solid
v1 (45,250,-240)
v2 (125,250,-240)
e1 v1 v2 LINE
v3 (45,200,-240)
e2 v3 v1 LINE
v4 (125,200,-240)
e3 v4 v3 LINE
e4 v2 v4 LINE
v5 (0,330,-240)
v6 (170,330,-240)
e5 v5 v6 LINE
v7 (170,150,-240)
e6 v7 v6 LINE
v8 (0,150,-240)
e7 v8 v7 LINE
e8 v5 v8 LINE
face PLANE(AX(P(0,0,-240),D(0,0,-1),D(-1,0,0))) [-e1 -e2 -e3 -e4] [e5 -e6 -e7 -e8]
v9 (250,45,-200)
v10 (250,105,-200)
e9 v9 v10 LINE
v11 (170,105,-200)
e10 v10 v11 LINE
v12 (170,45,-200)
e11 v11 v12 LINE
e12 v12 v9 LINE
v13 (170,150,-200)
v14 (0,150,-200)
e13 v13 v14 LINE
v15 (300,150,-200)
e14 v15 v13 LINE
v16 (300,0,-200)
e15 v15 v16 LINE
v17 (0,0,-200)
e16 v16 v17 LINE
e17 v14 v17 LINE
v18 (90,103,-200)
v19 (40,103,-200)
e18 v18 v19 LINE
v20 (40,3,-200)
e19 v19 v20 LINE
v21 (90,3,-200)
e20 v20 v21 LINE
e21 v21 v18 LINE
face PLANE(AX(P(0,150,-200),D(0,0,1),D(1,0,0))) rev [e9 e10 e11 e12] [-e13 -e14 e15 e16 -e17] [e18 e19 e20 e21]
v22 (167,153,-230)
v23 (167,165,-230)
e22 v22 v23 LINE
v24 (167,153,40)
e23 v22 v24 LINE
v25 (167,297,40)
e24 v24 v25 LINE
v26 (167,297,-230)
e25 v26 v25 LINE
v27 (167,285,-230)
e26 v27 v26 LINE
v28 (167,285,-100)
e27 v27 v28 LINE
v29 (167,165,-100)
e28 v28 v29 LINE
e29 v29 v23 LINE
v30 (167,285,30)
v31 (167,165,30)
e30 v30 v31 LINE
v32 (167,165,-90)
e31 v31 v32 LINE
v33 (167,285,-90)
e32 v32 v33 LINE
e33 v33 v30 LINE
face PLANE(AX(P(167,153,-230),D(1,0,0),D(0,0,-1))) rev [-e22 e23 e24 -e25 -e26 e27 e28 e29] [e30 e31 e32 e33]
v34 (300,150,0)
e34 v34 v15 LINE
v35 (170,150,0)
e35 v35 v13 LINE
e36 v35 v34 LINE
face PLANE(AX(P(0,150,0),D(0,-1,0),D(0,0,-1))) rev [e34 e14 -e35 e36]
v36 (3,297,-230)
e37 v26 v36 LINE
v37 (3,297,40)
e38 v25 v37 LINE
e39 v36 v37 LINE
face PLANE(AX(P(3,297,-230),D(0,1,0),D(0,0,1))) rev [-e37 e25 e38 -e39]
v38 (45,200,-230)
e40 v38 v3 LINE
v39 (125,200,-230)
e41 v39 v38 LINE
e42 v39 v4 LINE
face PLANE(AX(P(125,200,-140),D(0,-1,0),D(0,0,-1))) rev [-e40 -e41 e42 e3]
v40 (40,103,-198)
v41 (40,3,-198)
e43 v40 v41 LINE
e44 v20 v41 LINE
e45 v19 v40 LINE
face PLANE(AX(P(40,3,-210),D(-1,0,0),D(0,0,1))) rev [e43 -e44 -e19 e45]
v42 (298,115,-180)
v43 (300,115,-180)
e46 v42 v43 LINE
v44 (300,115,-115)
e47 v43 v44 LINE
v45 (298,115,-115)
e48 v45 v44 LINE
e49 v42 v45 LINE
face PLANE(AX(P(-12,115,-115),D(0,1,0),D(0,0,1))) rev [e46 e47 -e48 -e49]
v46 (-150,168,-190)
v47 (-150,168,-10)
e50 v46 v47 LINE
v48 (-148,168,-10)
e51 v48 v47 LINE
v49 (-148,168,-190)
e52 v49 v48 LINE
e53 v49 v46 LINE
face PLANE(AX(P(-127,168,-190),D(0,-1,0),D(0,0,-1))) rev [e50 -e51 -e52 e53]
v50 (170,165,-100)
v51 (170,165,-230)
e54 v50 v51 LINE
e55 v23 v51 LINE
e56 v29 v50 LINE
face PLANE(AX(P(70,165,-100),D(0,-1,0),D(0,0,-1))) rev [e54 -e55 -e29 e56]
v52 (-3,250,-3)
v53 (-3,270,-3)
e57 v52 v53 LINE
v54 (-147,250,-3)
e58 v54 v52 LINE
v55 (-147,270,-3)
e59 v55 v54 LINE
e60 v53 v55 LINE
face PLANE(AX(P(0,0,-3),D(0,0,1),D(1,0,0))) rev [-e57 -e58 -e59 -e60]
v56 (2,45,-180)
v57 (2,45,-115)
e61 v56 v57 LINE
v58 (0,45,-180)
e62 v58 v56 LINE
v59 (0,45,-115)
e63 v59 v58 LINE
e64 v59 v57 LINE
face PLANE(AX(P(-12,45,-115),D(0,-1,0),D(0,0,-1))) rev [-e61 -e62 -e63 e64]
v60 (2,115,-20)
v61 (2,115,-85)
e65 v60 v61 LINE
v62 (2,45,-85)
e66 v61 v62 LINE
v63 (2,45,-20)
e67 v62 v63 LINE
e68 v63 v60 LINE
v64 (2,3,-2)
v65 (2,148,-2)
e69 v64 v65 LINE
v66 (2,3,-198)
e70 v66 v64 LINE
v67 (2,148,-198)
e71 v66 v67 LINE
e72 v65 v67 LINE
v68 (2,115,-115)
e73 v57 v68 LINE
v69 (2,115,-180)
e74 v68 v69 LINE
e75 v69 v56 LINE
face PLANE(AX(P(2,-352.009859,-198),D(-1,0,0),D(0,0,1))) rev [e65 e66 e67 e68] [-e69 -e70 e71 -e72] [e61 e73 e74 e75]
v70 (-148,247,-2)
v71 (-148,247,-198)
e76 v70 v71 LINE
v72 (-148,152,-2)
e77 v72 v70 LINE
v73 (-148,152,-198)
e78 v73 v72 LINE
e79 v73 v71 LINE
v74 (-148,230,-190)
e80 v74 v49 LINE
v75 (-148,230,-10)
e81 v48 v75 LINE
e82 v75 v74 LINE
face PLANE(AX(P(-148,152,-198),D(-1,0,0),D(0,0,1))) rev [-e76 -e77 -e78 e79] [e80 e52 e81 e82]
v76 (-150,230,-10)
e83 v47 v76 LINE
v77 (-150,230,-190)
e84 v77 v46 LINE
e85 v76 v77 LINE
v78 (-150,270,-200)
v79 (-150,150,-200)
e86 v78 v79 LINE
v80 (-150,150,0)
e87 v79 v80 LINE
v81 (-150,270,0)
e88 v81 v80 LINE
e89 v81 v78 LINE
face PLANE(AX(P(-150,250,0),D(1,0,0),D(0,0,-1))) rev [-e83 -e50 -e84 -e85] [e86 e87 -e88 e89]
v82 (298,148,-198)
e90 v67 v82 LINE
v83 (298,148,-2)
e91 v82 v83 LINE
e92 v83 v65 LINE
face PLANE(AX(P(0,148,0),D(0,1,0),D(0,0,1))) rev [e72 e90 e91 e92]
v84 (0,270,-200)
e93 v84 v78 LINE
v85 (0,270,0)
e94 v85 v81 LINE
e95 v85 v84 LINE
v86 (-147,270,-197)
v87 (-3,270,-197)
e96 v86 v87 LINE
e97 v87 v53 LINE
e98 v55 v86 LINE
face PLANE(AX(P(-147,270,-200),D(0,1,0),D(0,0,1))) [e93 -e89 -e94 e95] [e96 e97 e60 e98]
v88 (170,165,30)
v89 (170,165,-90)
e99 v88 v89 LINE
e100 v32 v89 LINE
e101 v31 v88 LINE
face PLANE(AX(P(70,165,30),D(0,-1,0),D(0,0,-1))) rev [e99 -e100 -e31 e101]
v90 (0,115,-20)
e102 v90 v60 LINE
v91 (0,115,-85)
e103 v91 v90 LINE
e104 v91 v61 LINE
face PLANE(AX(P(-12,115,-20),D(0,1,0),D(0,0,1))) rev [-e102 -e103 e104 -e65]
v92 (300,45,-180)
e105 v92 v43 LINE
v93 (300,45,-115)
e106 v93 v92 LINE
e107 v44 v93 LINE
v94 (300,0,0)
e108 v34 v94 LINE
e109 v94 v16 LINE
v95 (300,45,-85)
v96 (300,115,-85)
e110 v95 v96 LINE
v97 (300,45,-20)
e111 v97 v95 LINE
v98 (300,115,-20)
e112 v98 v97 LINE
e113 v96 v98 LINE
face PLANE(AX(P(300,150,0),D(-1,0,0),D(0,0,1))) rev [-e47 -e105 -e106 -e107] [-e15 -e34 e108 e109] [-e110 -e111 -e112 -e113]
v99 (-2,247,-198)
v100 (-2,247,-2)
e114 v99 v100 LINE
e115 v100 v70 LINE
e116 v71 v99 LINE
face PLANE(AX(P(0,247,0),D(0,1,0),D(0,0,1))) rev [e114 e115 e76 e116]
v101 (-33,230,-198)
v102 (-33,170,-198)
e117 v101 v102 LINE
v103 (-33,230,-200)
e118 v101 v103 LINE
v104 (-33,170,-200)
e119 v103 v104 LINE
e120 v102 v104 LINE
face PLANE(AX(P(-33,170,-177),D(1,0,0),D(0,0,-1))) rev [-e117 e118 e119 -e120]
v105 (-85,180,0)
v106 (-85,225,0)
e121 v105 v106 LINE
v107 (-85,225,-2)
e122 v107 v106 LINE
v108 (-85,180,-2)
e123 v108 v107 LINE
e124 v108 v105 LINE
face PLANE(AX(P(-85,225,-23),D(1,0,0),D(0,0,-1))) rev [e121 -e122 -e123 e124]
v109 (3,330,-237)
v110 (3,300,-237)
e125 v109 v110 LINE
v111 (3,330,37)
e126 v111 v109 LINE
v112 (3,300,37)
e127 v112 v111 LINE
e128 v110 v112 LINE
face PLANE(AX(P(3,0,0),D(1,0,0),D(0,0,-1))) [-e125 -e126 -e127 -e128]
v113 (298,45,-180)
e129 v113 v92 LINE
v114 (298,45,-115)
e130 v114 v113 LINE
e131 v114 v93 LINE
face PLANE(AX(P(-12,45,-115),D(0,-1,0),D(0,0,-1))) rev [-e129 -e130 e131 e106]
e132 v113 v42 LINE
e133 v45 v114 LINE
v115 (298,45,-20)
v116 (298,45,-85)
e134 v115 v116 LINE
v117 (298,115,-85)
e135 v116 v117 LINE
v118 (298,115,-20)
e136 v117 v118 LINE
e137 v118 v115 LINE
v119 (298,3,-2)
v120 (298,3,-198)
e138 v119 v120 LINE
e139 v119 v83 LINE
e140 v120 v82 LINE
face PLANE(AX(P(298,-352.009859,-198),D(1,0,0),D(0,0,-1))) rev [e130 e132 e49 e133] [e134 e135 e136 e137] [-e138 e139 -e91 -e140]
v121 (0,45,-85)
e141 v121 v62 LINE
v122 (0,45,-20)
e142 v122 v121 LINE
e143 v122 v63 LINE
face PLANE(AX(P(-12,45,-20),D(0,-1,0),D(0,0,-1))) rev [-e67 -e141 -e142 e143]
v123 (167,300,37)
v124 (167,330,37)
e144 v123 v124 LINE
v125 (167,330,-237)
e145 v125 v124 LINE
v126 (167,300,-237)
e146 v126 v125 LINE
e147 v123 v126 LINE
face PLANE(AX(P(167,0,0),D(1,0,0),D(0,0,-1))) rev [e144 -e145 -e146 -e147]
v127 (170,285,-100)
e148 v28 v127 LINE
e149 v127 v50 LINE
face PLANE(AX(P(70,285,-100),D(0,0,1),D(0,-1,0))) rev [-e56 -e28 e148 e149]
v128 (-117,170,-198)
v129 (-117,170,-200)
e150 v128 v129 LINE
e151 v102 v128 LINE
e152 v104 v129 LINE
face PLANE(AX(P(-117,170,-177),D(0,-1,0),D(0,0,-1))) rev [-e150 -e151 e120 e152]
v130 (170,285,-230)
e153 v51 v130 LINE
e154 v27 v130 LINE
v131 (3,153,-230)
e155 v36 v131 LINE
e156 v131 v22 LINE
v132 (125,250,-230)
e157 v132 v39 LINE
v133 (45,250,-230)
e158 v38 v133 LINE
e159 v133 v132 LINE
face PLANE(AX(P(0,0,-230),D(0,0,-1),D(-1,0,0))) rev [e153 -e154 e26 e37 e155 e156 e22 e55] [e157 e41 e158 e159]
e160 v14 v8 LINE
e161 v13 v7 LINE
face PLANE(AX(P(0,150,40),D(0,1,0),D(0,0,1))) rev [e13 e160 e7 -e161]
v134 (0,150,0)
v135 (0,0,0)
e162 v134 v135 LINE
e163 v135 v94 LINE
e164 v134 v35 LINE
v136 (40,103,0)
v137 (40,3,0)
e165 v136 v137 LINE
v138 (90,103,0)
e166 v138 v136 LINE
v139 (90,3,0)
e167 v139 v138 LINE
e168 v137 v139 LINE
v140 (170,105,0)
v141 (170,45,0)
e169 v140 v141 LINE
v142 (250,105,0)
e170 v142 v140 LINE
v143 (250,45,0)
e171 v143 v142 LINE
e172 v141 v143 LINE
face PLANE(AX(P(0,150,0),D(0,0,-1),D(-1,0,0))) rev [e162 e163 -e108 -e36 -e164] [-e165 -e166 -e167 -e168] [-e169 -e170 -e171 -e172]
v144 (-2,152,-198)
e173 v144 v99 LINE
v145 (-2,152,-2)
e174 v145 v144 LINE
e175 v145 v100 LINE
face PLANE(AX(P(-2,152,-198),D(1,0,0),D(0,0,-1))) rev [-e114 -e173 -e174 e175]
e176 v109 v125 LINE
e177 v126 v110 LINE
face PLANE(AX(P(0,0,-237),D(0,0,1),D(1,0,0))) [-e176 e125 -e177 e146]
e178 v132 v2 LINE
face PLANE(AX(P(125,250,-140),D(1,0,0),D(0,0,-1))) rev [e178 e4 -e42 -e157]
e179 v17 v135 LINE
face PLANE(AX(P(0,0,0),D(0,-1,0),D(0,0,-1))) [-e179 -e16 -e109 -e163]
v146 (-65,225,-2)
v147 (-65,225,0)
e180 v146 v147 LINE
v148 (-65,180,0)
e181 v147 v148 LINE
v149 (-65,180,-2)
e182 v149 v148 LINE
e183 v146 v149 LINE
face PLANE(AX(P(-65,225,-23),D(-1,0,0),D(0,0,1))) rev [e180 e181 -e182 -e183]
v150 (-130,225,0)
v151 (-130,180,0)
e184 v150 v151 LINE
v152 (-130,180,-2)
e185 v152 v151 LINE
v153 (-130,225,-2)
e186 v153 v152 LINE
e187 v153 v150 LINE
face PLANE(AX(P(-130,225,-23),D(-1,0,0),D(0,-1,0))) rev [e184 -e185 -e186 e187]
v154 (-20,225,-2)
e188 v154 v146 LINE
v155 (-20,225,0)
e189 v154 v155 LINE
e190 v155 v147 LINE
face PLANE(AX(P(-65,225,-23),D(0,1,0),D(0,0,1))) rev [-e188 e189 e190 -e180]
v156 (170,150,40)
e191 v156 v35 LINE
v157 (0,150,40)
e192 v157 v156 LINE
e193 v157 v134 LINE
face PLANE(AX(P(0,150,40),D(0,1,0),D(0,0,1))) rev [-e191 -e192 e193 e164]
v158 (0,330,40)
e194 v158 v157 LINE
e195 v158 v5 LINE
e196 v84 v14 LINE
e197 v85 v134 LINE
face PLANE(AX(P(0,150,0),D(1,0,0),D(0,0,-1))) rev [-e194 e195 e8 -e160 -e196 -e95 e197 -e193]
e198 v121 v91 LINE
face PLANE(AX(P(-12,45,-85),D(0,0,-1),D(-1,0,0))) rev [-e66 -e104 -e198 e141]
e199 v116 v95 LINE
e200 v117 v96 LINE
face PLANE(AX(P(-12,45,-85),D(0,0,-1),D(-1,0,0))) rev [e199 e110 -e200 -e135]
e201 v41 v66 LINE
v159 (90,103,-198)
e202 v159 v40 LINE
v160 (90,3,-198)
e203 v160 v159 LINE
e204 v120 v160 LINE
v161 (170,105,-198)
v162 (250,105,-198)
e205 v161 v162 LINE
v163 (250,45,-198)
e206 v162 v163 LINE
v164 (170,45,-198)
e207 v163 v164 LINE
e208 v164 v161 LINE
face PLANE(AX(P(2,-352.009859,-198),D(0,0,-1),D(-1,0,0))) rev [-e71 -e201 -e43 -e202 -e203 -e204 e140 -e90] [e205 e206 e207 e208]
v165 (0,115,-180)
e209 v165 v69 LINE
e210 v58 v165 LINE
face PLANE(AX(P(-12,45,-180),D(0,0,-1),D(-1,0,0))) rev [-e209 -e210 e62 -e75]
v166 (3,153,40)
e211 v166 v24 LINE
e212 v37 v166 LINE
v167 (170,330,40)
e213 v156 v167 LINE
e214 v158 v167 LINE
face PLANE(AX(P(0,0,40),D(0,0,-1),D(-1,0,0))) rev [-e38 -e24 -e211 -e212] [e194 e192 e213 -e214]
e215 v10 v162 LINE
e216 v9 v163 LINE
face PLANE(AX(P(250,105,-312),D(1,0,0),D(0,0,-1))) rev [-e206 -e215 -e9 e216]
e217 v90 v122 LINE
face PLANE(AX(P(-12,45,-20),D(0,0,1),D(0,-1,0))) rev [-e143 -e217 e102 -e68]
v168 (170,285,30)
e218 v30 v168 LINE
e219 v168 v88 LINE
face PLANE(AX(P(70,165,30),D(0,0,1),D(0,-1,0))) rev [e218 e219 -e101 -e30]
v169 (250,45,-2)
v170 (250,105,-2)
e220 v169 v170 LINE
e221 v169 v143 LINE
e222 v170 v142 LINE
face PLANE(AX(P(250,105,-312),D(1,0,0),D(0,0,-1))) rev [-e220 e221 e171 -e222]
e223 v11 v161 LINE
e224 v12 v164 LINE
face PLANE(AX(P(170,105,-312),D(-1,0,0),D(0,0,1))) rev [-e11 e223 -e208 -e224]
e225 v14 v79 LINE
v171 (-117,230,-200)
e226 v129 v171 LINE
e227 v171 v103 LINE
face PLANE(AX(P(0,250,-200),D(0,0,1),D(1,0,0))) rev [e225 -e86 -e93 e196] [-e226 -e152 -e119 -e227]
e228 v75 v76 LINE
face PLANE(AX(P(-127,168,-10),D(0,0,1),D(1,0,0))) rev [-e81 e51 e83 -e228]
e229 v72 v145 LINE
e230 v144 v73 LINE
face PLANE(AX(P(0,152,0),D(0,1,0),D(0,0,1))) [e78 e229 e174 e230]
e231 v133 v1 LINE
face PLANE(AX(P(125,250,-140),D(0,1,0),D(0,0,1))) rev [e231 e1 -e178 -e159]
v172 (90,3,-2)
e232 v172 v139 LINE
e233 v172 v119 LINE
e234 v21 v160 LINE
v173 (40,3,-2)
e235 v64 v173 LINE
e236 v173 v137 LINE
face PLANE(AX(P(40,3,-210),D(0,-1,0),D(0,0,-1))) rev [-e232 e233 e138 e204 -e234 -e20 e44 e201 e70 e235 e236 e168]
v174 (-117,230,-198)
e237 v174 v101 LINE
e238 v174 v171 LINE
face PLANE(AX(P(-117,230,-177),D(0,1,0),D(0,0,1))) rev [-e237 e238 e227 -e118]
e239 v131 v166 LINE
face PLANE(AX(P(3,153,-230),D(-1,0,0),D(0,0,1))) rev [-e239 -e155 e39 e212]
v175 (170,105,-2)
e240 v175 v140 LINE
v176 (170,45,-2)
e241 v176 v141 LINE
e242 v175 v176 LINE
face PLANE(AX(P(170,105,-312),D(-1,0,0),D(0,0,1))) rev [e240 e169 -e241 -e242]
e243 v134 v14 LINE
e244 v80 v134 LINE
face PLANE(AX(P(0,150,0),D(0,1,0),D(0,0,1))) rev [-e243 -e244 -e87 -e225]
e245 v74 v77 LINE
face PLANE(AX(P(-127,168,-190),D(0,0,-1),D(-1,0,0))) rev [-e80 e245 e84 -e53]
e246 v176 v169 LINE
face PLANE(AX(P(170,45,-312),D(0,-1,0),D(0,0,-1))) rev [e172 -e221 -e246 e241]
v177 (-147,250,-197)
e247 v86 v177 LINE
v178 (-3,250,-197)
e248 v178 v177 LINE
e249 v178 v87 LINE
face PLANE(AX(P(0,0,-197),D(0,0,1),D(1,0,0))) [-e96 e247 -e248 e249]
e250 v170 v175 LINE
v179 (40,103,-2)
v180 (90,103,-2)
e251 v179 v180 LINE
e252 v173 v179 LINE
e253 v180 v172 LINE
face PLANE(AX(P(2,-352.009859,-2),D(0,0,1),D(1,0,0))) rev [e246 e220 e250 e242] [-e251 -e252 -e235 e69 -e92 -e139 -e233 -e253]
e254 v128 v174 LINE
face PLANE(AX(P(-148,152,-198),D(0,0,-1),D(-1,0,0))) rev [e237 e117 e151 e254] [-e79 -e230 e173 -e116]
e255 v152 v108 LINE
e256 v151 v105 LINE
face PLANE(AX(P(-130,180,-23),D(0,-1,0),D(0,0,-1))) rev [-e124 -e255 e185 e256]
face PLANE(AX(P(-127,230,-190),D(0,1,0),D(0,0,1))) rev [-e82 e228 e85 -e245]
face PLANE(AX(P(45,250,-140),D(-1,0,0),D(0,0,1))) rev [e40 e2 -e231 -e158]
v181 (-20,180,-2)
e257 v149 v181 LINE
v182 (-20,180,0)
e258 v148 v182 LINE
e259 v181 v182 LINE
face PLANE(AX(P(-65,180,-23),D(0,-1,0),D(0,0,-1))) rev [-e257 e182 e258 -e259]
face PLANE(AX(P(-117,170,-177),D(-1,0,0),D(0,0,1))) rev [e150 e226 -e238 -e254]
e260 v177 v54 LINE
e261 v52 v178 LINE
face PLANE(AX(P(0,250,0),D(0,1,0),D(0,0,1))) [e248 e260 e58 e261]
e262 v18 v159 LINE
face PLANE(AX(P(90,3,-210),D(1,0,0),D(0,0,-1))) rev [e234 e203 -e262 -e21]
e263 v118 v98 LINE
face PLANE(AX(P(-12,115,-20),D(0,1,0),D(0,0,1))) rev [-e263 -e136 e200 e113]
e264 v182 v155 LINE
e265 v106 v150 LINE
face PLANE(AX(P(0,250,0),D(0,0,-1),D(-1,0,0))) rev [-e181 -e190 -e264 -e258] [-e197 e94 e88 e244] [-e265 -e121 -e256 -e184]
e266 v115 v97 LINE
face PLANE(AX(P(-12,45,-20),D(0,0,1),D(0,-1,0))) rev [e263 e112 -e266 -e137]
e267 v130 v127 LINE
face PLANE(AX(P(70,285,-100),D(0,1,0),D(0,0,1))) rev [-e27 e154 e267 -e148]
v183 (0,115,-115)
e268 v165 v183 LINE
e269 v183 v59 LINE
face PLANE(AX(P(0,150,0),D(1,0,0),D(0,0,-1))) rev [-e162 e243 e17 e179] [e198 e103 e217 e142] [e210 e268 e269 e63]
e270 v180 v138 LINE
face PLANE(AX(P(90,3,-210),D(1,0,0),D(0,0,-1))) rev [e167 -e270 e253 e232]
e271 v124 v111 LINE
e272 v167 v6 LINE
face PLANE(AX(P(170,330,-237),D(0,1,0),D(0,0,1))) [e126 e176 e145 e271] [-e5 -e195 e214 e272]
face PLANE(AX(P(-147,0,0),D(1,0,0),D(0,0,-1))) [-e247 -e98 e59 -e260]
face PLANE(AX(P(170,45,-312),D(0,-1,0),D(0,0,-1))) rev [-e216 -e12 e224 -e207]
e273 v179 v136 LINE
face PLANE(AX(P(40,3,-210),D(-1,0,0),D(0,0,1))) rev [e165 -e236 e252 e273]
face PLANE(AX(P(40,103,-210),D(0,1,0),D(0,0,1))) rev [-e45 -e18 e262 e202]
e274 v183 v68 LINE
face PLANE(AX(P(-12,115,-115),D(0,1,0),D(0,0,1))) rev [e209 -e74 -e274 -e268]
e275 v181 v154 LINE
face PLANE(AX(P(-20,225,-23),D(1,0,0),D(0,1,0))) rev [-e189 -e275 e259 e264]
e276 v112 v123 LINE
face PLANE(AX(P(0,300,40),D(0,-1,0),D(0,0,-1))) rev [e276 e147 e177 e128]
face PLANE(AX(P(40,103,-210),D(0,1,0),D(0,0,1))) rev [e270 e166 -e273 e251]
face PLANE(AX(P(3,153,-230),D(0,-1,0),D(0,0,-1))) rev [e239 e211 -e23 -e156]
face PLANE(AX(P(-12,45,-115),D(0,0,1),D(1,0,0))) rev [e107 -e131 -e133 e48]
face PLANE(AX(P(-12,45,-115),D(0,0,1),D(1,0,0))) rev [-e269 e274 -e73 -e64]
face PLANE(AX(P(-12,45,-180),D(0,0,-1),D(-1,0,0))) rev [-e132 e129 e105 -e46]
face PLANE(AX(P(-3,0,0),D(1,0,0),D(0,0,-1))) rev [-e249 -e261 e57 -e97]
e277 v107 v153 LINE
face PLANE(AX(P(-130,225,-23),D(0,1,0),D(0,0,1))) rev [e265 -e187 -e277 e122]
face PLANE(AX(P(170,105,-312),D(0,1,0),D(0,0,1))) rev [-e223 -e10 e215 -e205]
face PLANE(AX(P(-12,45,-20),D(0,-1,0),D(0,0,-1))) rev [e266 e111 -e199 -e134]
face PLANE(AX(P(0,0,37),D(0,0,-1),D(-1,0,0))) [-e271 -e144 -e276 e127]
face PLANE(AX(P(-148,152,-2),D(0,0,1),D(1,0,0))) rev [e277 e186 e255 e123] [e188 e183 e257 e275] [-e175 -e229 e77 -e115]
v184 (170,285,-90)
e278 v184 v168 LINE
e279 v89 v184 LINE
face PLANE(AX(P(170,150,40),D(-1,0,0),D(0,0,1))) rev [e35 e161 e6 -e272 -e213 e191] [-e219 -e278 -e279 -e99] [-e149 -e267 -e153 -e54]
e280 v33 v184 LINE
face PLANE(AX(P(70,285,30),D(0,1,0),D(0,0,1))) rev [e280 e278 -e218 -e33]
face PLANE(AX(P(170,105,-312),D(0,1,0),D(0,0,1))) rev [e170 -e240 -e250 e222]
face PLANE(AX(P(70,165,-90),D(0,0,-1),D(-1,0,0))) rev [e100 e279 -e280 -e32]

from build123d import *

# Parameters (mm, degrees)
GROUND_FLOOR_FOOTPRINT_SKETCH_W     = 300
GROUND_FLOOR_FOOTPRINT_SKETCH_H     = 200
GROUND_FLOOR_BLOCK_DEPTH            = 150
GROUND_FLOOR_DOOR_SKETCH_W          = 50
GROUND_FLOOR_DOOR_SKETCH_H          = 100
GROUND_FLOOR_DOOR_OPENING_DEPTH     = 210
GROUND_FLOOR_INTERIOR_POCKET_REACH  = 392.512
GROUND_FLOOR_INTERIOR_SKETCH_W      = 296
GROUND_FLOOR_INTERIOR_SKETCH_H      = 196
GROUND_FLOOR_SLAB_SKETCH_W          = 300
GROUND_FLOOR_SLAB_SKETCH_H          = 200
GROUND_FLOOR_SLAB_DEPTH             = 2
GROUND_FLOOR_WINDOW_SKETCH_W        = 80
GROUND_FLOOR_WINDOW_SKETCH_H        = 60
GROUND_FLOOR_WINDOW_DEPTH           = 312
GROUND_FLOOR_SIDE_WINDOWS_SKETCH_W  = 65
GROUND_FLOOR_SIDE_WINDOWS_SKETCH_H  = 70
GROUND_FLOOR_SIDE_WINDOWS_DEPTH     = 312
FIRST_FLOOR_FOOTPRINT_SKETCH_W      = 150
FIRST_FLOOR_FOOTPRINT_SKETCH_H      = 200
FIRST_FLOOR_BLOCK_DEPTH             = 100
FIRST_FLOOR_INTERIOR_SKETCH_W       = 146
FIRST_FLOOR_INTERIOR_SKETCH_H       = 196
FIRST_FLOOR_INTERIOR_POCKET_DEPTH   = 98
FIRST_FLOOR_SLAB_SKETCH_W           = 150
FIRST_FLOOR_SLAB_SKETCH_H           = 200
FIRST_FLOOR_SLAB_DEPTH              = 3
FIRST_FLOOR_DOOR_SKETCH_W           = 180
FIRST_FLOOR_DOOR_SKETCH_H           = 62
FIRST_FLOOR_DOOR_OPENING_DEPTH      = 23
FIRST_FLOOR_TWIN_WINDOWS_SKETCH_W   = 45
FIRST_FLOOR_TWIN_WINDOWS_SKETCH_H   = 45
FIRST_FLOOR_TWIN_WINDOWS_DEPTH      = 23
FIRST_FLOOR_WINDOW_SKETCH_W         = 84
FIRST_FLOOR_WINDOW_SKETCH_H         = 60
FIRST_FLOOR_WINDOW_DEPTH            = 23
FIRST_FLOOR_PARAPET_FRONT_SKETCH_W  = 200
FIRST_FLOOR_PARAPET_FRONT_SKETCH_H  = 20
FIRST_FLOOR_PARAPET_FRONT_DEPTH     = 3
FIRST_FLOOR_PARAPET_SIDE_1_SKETCH_W = 150
FIRST_FLOOR_PARAPET_SIDE_1_SKETCH_H = 20
FIRST_FLOOR_PARAPET_SIDE_1_DEPTH    = 3
FIRST_FLOOR_PARAPET_SIDE_2_SKETCH_W = 150
FIRST_FLOOR_PARAPET_SIDE_2_SKETCH_H = 20
FIRST_FLOOR_PARAPET_SIDE_2_DEPTH    = 3
FIRST_FLOOR_PARAPET_REAR_SKETCH_W   = 197
FIRST_FLOOR_PARAPET_REAR_SKETCH_H   = 20
FIRST_FLOOR_PARAPET_REAR_DEPTH      = 3
UPPER_FLOOR_BLOCK_DEPTH             = 40
UPPER_FLOOR_BLOCK_DEPTH_BACK        = 240
UPPER_FLOOR_PROFILE_SKETCH_W        = 170
UPPER_FLOOR_PROFILE_SKETCH_H        = 150
UPPER_FLOOR_INTERIOR_SKETCH_W       = 164
UPPER_FLOOR_INTERIOR_SKETCH_H       = 144
UPPER_FLOOR_INTERIOR_POCKET_DEPTH   = 270
UPPER_FLOOR_OPENING_1_SKETCH_W      = 120
UPPER_FLOOR_OPENING_1_SKETCH_H      = 120
UPPER_FLOOR_OPENING_1_DEPTH         = 100
UPPER_FLOOR_OPENING_2_SKETCH_W      = 130
UPPER_FLOOR_OPENING_2_SKETCH_H      = 120
UPPER_FLOOR_OPENING_2_DEPTH         = 100
UPPER_FLOOR_WINDOW_SKETCH_W         = 80
UPPER_FLOOR_WINDOW_SKETCH_H         = 50
UPPER_FLOOR_WINDOW_DEPTH            = 100
UPPER_FLOOR_PARAPET_FRONT_SKETCH_W  = 170
UPPER_FLOOR_PARAPET_FRONT_SKETCH_H  = 30
UPPER_FLOOR_PARAPET_FRONT_DEPTH     = 3
UPPER_FLOOR_PARAPET_SIDE_1_SKETCH_W = 277
UPPER_FLOOR_PARAPET_SIDE_1_SKETCH_H = 30
UPPER_FLOOR_PARAPET_SIDE_1_DEPTH    = 3
UPPER_FLOOR_PARAPET_SIDE_2_SKETCH_W = 170
UPPER_FLOOR_PARAPET_SIDE_2_SKETCH_H = 30
UPPER_FLOOR_PARAPET_SIDE_2_DEPTH    = 3
UPPER_FLOOR_PARAPET_REAR_SKETCH_W   = 274
UPPER_FLOOR_PARAPET_REAR_SKETCH_H   = 30
UPPER_FLOOR_PARAPET_REAR_DEPTH      = 3


with BuildPart() as part:
    # Ground Floor Footprint Sketch → Ground Floor Block (new body)
    with BuildSketch(Plane(origin=(0, 0, 0), x_dir=(1, 0, 0), z_dir=(0, 1, 0))):
        with Locations((150, 100)):
            Rectangle(GROUND_FLOOR_FOOTPRINT_SKETCH_W, GROUND_FLOOR_FOOTPRINT_SKETCH_H)
    extrude(amount=GROUND_FLOOR_BLOCK_DEPTH)

    # Ground Floor Door Sketch → Ground Floor Door Opening (cut)
    with BuildSketch(Plane.XY):
        with Locations((65, 53)):
            Rectangle(GROUND_FLOOR_DOOR_SKETCH_W, GROUND_FLOOR_DOOR_SKETCH_H)
    extrude(amount=-GROUND_FLOOR_DOOR_OPENING_DEPTH, mode=Mode.SUBTRACT)

    # Ground Floor Interior Pocket: up to this face of the body (flat: up to its plane)
    ground_floor_interior_pocket_end = Plane(part.part.faces().sort_by_distance((65, 3, -100))[0])
    # Ground Floor Interior Sketch → Ground Floor Interior Pocket (cut, up to the picked face)
    with BuildSketch(Plane(origin=(0, 150, 0), x_dir=(1, 0, 0), z_dir=(0, 1, 0)), mode=Mode.PRIVATE) as ground_floor_interior_pocket_sk1:
        with Locations((150, 100)):
            Rectangle(GROUND_FLOOR_INTERIOR_SKETCH_W, GROUND_FLOOR_INTERIOR_SKETCH_H)
    ground_floor_interior_pocket_tool1 = split(extrude(ground_floor_interior_pocket_sk1.sketch, amount=-GROUND_FLOOR_INTERIOR_POCKET_REACH, mode=Mode.PRIVATE), bisect_by=ground_floor_interior_pocket_end, keep=Keep.BOTH, mode=Mode.PRIVATE)
    add(ground_floor_interior_pocket_tool1.solids().sort_by(Axis((150, 150, -100), (0, -1, 0)))[0], mode=Mode.SUBTRACT)

    # Ground Floor Slab Sketch → Ground Floor Slab (add)
    with BuildSketch(Plane(origin=(0, 150, 0), x_dir=(1, 0, 0), z_dir=(0, 1, 0))):
        with Locations((150, 100)):
            Rectangle(GROUND_FLOOR_SLAB_SKETCH_W, GROUND_FLOOR_SLAB_SKETCH_H)
    extrude(amount=-GROUND_FLOOR_SLAB_DEPTH)

    # Ground Floor Window Sketch → Ground Floor Window (cut)
    with BuildSketch(Plane.XY):
        with Locations((210, 75)):
            Rectangle(GROUND_FLOOR_WINDOW_SKETCH_W, GROUND_FLOOR_WINDOW_SKETCH_H)
    extrude(amount=-GROUND_FLOOR_WINDOW_DEPTH, mode=Mode.SUBTRACT)

    # Ground Floor Side Windows Sketch → Ground Floor Side Windows (cut)
    with BuildSketch(Plane(origin=(300, 0, 0), x_dir=(0, 0, -1), z_dir=(1, 0, 0))):
        with Locations((52.5, 80)):
            Rectangle(GROUND_FLOOR_SIDE_WINDOWS_SKETCH_W, GROUND_FLOOR_SIDE_WINDOWS_SKETCH_H)
        with Locations((147.5, 80)):
            Rectangle(GROUND_FLOOR_SIDE_WINDOWS_SKETCH_W, GROUND_FLOOR_SIDE_WINDOWS_SKETCH_H)
    extrude(amount=-GROUND_FLOOR_SIDE_WINDOWS_DEPTH, mode=Mode.SUBTRACT)



with BuildPart() as body_2:
    # First Floor Footprint Sketch → First Floor Block (new body)
    with BuildSketch(Plane(origin=(0, 150, 0), x_dir=(1, 0, 0), z_dir=(0, 1, 0))):
        with Locations((-75, 100)):
            Rectangle(FIRST_FLOOR_FOOTPRINT_SKETCH_W, FIRST_FLOOR_FOOTPRINT_SKETCH_H)
    extrude(amount=FIRST_FLOOR_BLOCK_DEPTH)

    # First Floor Interior Sketch → First Floor Interior Pocket (cut)
    with BuildSketch(Plane(origin=(0, 250, 0), x_dir=(1, 0, 0), z_dir=(0, 1, 0))):
        with Locations((-75, 100)):
            Rectangle(FIRST_FLOOR_INTERIOR_SKETCH_W, FIRST_FLOOR_INTERIOR_SKETCH_H)
    extrude(amount=-FIRST_FLOOR_INTERIOR_POCKET_DEPTH, mode=Mode.SUBTRACT)

    # First Floor Slab Sketch → First Floor Slab (add)
    with BuildSketch(Plane(origin=(0, 250, 0), x_dir=(1, 0, 0), z_dir=(0, 1, 0))):
        with Locations((-75, 100)):
            Rectangle(FIRST_FLOOR_SLAB_SKETCH_W, FIRST_FLOOR_SLAB_SKETCH_H)
    extrude(amount=-FIRST_FLOOR_SLAB_DEPTH)

    # First Floor Door Sketch → First Floor Door Opening (cut)
    with BuildSketch(Plane.ZY.offset(150)):
        with Locations((-100, 199)):
            Rectangle(FIRST_FLOOR_DOOR_SKETCH_W, FIRST_FLOOR_DOOR_SKETCH_H)
    extrude(amount=-FIRST_FLOOR_DOOR_OPENING_DEPTH, mode=Mode.SUBTRACT)

    # First Floor Twin Windows Sketch → First Floor Twin Windows (cut)
    with BuildSketch(Plane.XY):
        with Locations((-107.5, 202.5)):
            Rectangle(FIRST_FLOOR_TWIN_WINDOWS_SKETCH_W, FIRST_FLOOR_TWIN_WINDOWS_SKETCH_H)
        with Locations((-42.5, 202.5)):
            Rectangle(FIRST_FLOOR_TWIN_WINDOWS_SKETCH_W, FIRST_FLOOR_TWIN_WINDOWS_SKETCH_H)
    extrude(amount=-FIRST_FLOOR_TWIN_WINDOWS_DEPTH, mode=Mode.SUBTRACT)

    # First Floor Window Sketch → First Floor Window (cut)
    with BuildSketch(Plane(origin=(0, 0, -200), x_dir=(-1, 0, 0), z_dir=(0, 0, -1))):
        with Locations((75, 200)):
            Rectangle(FIRST_FLOOR_WINDOW_SKETCH_W, FIRST_FLOOR_WINDOW_SKETCH_H)
    extrude(amount=-FIRST_FLOOR_WINDOW_DEPTH, mode=Mode.SUBTRACT)

    # First Floor Parapet Front Sketch → First Floor Parapet Front (add)
    with BuildSketch(Plane.ZY.offset(150)):
        with Locations((-100, 260)):
            Rectangle(FIRST_FLOOR_PARAPET_FRONT_SKETCH_W, FIRST_FLOOR_PARAPET_FRONT_SKETCH_H)
    extrude(amount=-FIRST_FLOOR_PARAPET_FRONT_DEPTH)

    # First Floor Parapet Side 1 Sketch → First Floor Parapet Side 1 (add)
    with BuildSketch(Plane(origin=(0, 0, -200), x_dir=(-1, 0, 0), z_dir=(0, 0, -1))):
        with Locations((75, 260)):
            Rectangle(FIRST_FLOOR_PARAPET_SIDE_1_SKETCH_W, FIRST_FLOOR_PARAPET_SIDE_1_SKETCH_H)
    extrude(amount=-FIRST_FLOOR_PARAPET_SIDE_1_DEPTH)

    # First Floor Parapet Side 2 Sketch → First Floor Parapet Side 2 (add)
    with BuildSketch(Plane.XY):
        with Locations((-75, 260)):
            Rectangle(FIRST_FLOOR_PARAPET_SIDE_2_SKETCH_W, FIRST_FLOOR_PARAPET_SIDE_2_SKETCH_H)
    extrude(amount=-FIRST_FLOOR_PARAPET_SIDE_2_DEPTH)

    # First Floor Parapet Rear Sketch → First Floor Parapet Rear (add)
    with BuildSketch(Plane(origin=(0, 0, 0), x_dir=(0, 0, -1), z_dir=(1, 0, 0))):
        with Locations((98.5, 260)):
            Rectangle(FIRST_FLOOR_PARAPET_REAR_SKETCH_W, FIRST_FLOOR_PARAPET_REAR_SKETCH_H)
    extrude(amount=-FIRST_FLOOR_PARAPET_REAR_DEPTH)


with BuildPart() as part_1:
    add(part.part)

    add(body_2.part)  # Upper Floor Block merges body 2
    # Upper Floor Profile Sketch → Upper Floor Block (add, two sides: drawn at the far end of the back side and taken through both)
    with BuildSketch(Plane.XY.offset(-UPPER_FLOOR_BLOCK_DEPTH_BACK)):
        with Locations((85, 225)):
            Rectangle(UPPER_FLOOR_PROFILE_SKETCH_W, UPPER_FLOOR_PROFILE_SKETCH_H)
    extrude(amount=UPPER_FLOOR_BLOCK_DEPTH + UPPER_FLOOR_BLOCK_DEPTH_BACK)

    # Upper Floor Interior Sketch → Upper Floor Interior Pocket (cut)
    with BuildSketch(Plane.XY.offset(40)):
        with Locations((85, 225)):
            Rectangle(UPPER_FLOOR_INTERIOR_SKETCH_W, UPPER_FLOOR_INTERIOR_SKETCH_H)
    extrude(amount=-UPPER_FLOOR_INTERIOR_POCKET_DEPTH, mode=Mode.SUBTRACT)

    # Upper Floor Opening 1 Sketch → Upper Floor Opening 1 (cut)
    with BuildSketch(Plane(origin=(170, 0, 0), x_dir=(0, 0, -1), z_dir=(1, 0, 0))):
        with Locations((30, 225)):
            Rectangle(UPPER_FLOOR_OPENING_1_SKETCH_W, UPPER_FLOOR_OPENING_1_SKETCH_H)
    extrude(amount=-UPPER_FLOOR_OPENING_1_DEPTH, mode=Mode.SUBTRACT)

    # Upper Floor Opening 2 Sketch → Upper Floor Opening 2 (cut)
    with BuildSketch(Plane(origin=(170, 0, 0), x_dir=(0, 0, -1), z_dir=(1, 0, 0))):
        with Locations((165, 225)):
            Rectangle(UPPER_FLOOR_OPENING_2_SKETCH_W, UPPER_FLOOR_OPENING_2_SKETCH_H)
    extrude(amount=-UPPER_FLOOR_OPENING_2_DEPTH, mode=Mode.SUBTRACT)

    # Upper Floor Window Sketch → Upper Floor Window (cut)
    with BuildSketch(Plane(origin=(0, 0, -240), x_dir=(-1, 0, 0), z_dir=(0, 0, -1))):
        with Locations((-85, 225)):
            Rectangle(UPPER_FLOOR_WINDOW_SKETCH_W, UPPER_FLOOR_WINDOW_SKETCH_H)
    extrude(amount=-UPPER_FLOOR_WINDOW_DEPTH, mode=Mode.SUBTRACT)

    # Upper Floor Parapet Front Sketch → Upper Floor Parapet Front (add)
    with BuildSketch(Plane(origin=(0, 0, -240), x_dir=(-1, 0, 0), z_dir=(0, 0, -1))):
        with Locations((-85, 315)):
            Rectangle(UPPER_FLOOR_PARAPET_FRONT_SKETCH_W, UPPER_FLOOR_PARAPET_FRONT_SKETCH_H)
    extrude(amount=-UPPER_FLOOR_PARAPET_FRONT_DEPTH)

    # Upper Floor Parapet Side 1 Sketch → Upper Floor Parapet Side 1 (add)
    with BuildSketch(Plane(origin=(170, 0, 0), x_dir=(0, 0, -1), z_dir=(1, 0, 0))):
        with Locations((98.5, 315)):
            Rectangle(UPPER_FLOOR_PARAPET_SIDE_1_SKETCH_W, UPPER_FLOOR_PARAPET_SIDE_1_SKETCH_H)
    extrude(amount=-UPPER_FLOOR_PARAPET_SIDE_1_DEPTH)

    # Upper Floor Parapet Side 2 Sketch → Upper Floor Parapet Side 2 (add)
    with BuildSketch(Plane.XY.offset(40)):
        with Locations((85, 315)):
            Rectangle(UPPER_FLOOR_PARAPET_SIDE_2_SKETCH_W, UPPER_FLOOR_PARAPET_SIDE_2_SKETCH_H)
    extrude(amount=-UPPER_FLOOR_PARAPET_SIDE_2_DEPTH)

    # Upper Floor Parapet Rear Sketch → Upper Floor Parapet Rear (add)
    with BuildSketch(Plane.ZY):
        with Locations((-100, 315)):
            Rectangle(UPPER_FLOOR_PARAPET_REAR_SKETCH_W, UPPER_FLOOR_PARAPET_REAR_SKETCH_H)
    extrude(amount=-UPPER_FLOOR_PARAPET_REAR_DEPTH)


solid = part_1.part
